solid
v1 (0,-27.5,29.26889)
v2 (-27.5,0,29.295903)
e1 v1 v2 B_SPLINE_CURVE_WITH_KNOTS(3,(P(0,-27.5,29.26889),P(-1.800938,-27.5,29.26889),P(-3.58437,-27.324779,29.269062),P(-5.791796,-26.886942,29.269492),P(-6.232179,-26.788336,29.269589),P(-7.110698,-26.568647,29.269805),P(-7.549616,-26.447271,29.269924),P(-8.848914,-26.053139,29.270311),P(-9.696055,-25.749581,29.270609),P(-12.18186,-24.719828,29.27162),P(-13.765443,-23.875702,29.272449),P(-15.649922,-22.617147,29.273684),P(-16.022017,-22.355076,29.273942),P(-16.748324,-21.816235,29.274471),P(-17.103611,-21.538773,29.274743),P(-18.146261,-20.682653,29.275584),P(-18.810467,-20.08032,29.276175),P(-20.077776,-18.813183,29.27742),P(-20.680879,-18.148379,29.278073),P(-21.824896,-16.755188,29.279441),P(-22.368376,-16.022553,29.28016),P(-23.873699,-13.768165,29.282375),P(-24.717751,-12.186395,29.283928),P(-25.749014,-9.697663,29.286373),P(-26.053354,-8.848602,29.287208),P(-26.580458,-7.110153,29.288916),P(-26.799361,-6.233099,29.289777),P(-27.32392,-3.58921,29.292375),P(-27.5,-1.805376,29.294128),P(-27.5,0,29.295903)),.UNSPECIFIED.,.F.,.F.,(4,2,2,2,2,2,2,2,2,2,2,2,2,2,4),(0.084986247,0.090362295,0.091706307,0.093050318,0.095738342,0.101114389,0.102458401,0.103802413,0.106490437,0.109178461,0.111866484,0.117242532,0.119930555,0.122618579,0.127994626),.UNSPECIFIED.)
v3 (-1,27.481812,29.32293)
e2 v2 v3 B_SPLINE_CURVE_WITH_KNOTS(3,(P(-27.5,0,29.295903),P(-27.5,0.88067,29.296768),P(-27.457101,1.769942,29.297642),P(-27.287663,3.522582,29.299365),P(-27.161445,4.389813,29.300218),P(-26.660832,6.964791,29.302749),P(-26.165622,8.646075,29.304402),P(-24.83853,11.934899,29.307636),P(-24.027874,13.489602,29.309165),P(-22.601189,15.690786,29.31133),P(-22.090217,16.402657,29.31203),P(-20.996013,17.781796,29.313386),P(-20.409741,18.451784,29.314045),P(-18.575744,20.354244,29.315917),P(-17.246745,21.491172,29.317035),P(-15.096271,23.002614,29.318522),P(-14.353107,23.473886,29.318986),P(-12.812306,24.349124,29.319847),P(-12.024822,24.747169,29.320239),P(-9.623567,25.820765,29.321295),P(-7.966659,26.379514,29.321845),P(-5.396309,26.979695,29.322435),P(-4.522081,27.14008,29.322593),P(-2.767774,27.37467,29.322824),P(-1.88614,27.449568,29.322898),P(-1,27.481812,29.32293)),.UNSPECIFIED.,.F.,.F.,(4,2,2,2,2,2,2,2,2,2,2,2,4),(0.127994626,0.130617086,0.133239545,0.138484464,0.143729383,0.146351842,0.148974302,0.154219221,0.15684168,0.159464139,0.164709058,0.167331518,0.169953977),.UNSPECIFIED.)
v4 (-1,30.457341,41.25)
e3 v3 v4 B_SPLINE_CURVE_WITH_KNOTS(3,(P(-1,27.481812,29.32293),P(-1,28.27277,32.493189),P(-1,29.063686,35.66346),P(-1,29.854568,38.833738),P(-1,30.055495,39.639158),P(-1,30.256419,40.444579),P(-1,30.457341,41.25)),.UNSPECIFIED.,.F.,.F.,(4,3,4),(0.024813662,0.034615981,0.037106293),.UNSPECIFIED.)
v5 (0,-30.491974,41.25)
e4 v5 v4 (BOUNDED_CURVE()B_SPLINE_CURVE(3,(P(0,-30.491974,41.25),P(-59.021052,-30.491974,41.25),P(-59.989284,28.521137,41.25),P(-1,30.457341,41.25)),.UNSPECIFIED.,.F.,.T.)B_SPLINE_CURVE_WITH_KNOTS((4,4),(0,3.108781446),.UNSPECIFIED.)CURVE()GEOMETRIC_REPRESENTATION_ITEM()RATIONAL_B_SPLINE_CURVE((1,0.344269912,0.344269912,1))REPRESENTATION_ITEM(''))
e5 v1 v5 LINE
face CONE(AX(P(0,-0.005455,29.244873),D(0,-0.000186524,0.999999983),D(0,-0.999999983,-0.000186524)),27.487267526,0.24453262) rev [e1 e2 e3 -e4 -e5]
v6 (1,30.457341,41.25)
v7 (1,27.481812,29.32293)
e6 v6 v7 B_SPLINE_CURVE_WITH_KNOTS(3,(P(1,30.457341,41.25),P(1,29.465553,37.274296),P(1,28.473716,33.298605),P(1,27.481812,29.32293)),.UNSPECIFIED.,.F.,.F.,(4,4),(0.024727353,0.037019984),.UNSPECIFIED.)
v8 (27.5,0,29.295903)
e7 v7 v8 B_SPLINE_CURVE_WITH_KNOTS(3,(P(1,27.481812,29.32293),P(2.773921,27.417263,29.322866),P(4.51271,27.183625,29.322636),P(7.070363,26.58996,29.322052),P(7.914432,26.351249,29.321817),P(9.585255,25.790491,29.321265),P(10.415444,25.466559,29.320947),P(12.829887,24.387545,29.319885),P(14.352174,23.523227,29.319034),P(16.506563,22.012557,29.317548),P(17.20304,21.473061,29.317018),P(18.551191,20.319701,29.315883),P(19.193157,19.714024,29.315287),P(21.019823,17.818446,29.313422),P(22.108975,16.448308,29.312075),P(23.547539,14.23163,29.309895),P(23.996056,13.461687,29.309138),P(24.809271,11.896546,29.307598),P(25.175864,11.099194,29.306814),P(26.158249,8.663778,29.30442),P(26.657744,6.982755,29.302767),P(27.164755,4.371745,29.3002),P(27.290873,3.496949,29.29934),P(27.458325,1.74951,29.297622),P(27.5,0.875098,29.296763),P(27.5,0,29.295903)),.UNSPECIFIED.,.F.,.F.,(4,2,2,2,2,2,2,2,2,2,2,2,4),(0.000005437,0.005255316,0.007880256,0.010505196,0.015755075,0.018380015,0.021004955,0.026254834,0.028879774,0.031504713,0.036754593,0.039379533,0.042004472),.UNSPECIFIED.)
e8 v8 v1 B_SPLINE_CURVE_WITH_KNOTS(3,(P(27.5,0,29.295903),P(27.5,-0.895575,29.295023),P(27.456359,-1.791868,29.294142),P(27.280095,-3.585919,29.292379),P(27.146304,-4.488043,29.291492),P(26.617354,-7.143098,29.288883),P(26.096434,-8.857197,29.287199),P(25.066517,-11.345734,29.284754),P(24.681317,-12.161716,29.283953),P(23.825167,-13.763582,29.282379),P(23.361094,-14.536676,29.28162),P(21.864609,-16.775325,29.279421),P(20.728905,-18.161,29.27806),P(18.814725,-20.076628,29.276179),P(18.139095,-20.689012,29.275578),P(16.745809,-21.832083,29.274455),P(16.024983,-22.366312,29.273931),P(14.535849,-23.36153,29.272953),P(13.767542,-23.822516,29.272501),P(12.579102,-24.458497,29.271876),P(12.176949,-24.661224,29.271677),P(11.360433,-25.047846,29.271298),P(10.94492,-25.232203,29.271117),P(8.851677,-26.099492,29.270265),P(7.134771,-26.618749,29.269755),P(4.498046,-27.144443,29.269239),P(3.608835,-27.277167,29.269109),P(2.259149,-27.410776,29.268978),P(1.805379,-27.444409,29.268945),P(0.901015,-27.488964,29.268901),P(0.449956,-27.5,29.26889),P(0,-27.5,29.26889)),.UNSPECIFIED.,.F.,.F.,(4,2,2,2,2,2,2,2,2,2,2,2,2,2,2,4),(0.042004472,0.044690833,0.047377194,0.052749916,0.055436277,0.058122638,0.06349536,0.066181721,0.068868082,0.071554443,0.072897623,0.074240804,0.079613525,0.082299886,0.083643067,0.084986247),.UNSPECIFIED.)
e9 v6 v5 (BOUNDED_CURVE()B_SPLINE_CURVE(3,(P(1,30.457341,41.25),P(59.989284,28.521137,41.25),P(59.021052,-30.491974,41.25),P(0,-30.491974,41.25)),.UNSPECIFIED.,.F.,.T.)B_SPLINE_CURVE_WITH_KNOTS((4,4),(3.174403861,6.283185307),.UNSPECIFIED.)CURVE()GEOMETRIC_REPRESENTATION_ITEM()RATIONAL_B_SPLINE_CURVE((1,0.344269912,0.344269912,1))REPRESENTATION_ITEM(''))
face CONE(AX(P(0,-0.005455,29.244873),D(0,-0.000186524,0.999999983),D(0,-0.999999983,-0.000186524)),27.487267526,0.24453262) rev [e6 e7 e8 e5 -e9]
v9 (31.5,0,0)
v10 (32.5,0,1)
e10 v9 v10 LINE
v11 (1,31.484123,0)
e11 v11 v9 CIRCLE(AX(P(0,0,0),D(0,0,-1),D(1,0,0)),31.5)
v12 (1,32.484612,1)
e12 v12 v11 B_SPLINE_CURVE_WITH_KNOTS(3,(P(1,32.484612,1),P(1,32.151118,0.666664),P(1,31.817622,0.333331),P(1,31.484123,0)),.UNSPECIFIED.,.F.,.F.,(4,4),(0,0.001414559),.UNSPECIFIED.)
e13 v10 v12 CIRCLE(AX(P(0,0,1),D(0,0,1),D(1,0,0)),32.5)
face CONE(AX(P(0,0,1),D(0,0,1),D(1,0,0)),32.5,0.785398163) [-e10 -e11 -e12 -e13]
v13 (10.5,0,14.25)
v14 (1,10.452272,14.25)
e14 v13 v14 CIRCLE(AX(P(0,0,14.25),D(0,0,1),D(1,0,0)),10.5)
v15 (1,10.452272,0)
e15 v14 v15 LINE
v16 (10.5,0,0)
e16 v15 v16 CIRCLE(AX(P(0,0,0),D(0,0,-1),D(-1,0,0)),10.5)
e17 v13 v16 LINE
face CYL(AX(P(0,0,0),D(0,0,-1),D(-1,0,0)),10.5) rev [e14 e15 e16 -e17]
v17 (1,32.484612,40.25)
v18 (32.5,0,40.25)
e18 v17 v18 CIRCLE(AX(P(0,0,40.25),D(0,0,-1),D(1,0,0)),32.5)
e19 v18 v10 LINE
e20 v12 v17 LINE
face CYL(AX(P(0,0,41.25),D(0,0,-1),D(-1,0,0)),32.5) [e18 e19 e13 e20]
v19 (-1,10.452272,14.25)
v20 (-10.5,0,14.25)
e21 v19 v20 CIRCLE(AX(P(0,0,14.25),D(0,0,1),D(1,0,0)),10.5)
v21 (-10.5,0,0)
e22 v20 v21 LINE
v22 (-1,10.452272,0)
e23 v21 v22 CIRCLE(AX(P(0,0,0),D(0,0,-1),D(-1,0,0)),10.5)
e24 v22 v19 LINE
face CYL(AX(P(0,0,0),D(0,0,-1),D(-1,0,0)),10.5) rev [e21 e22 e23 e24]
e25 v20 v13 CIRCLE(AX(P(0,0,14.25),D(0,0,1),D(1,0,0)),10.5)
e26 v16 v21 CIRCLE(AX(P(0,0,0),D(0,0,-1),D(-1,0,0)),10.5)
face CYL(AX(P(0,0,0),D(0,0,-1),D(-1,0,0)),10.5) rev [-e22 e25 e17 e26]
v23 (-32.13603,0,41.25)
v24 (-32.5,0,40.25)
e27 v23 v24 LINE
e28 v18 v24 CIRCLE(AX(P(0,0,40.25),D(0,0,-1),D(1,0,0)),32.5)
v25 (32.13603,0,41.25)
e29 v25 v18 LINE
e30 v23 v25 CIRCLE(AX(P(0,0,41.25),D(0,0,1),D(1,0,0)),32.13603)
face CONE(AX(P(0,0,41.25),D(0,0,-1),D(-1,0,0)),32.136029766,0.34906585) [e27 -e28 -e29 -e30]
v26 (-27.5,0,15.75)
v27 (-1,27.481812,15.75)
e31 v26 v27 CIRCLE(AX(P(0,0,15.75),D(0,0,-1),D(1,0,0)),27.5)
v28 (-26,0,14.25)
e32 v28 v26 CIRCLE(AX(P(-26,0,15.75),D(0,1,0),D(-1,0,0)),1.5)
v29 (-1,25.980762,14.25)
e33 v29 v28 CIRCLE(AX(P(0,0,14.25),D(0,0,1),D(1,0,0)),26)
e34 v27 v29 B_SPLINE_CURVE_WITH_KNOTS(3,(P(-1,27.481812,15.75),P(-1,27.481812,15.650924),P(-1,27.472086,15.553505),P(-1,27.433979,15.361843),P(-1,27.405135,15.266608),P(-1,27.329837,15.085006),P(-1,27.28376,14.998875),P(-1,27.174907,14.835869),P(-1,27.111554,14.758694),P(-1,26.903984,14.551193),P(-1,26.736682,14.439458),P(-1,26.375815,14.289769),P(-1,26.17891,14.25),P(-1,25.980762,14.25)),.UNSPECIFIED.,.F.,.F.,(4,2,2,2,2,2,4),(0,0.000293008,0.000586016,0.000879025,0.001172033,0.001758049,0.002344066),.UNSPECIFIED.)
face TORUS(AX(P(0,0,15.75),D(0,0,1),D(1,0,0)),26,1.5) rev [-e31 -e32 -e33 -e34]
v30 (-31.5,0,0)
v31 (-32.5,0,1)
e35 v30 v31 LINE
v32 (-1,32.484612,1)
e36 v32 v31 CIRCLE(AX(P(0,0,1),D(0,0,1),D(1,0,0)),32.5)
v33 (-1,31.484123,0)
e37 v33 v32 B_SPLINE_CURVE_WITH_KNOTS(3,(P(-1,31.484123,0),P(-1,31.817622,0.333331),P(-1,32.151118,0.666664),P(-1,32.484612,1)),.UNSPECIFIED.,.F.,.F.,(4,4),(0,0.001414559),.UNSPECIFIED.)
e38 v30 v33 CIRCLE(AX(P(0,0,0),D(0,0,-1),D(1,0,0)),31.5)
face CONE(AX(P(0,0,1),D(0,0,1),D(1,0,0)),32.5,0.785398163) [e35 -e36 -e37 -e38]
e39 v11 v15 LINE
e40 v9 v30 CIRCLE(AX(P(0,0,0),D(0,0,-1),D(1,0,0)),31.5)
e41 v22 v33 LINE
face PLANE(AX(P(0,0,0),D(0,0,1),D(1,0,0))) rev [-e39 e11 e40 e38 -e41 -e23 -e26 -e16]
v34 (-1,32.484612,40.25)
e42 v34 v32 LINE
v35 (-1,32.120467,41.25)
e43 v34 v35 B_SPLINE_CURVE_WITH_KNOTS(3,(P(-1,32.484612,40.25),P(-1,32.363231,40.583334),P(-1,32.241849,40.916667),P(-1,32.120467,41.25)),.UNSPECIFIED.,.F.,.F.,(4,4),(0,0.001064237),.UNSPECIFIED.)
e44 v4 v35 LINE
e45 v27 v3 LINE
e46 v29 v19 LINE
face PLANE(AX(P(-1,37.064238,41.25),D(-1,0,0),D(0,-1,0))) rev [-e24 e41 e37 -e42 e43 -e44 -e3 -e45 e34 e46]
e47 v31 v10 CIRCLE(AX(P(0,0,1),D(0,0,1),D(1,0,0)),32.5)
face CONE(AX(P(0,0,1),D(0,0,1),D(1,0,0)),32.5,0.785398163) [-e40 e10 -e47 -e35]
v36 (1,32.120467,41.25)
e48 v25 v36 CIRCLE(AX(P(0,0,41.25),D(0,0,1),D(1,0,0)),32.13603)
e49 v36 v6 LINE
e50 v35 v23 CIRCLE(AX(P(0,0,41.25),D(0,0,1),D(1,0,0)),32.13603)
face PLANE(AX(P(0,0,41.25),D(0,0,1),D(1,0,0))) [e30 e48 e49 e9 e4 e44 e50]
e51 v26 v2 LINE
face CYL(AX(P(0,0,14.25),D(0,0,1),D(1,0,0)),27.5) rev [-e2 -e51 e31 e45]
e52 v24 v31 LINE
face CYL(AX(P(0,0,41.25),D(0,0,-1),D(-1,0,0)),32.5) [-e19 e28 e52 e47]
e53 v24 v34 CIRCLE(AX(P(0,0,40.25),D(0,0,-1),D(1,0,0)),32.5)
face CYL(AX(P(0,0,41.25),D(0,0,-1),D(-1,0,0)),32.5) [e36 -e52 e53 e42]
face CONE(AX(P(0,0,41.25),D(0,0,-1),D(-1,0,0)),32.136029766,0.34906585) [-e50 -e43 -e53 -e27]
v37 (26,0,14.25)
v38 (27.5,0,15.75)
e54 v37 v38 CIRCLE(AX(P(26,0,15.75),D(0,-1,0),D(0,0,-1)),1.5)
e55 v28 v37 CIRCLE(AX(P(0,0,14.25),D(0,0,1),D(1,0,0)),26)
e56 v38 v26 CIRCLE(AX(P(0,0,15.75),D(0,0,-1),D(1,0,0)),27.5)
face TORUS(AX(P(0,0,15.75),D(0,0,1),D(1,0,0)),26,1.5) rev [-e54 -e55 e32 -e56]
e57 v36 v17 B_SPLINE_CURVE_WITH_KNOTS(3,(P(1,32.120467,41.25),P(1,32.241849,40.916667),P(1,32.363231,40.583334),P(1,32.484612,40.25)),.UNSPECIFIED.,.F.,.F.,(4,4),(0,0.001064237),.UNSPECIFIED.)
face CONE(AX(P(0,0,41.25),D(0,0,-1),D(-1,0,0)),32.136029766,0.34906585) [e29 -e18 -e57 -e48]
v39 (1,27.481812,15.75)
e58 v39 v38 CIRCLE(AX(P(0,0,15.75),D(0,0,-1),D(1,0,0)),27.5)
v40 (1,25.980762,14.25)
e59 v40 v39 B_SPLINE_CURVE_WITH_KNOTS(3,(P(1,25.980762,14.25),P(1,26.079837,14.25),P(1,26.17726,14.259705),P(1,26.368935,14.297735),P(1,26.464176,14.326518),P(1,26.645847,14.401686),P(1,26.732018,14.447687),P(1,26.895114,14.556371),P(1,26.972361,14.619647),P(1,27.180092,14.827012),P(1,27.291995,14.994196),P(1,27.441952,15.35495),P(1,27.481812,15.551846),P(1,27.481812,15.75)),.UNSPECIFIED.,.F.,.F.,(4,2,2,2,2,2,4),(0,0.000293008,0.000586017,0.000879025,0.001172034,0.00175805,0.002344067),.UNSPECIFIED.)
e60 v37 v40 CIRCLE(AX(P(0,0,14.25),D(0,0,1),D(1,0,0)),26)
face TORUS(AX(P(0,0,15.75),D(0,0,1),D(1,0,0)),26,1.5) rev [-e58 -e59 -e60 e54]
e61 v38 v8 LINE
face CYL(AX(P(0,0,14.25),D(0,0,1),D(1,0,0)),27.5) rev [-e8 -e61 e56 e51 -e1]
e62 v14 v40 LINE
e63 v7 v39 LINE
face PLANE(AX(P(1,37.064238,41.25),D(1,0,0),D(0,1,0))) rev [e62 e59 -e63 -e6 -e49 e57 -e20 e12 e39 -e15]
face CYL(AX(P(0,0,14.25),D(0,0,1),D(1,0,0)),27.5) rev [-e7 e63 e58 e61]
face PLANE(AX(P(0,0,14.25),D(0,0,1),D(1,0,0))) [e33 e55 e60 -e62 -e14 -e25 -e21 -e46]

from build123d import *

# Parameters (mm, degrees)
SKETCH_1_R          = 32.5
EXTRUDE_1_DEPTH     = 41.25
SKETCH_2_R          = 27.5
CUT_EXTRUDE_1_DEPTH = 27
HOLE_WIZARD_M24_1_D = 21
SKETCH_4_W          = 2
SKETCH_4_H          = 41.62847608
CUT_EXTRUDE_2_DEPTH = 62.758096635
CHAMFER_1_SIZE      = 1
CHAMFER_2_SIZE      = 1
CHAMFER_2_SIZE2     = 0.363970234
FILLET_1_R          = 1.5


with BuildPart() as part:
    # 草图1 → 凸台-拉伸1 (new body)
    with BuildSketch(Plane.XY):
        Circle(SKETCH_1_R)
    extrude(amount=EXTRUDE_1_DEPTH)

    # 草图2 → 切除-拉伸1 (cut)
    with BuildSketch(Plane.XY.offset(41.25)):
        Circle(SKETCH_2_R)
    extrude(amount=-CUT_EXTRUDE_1_DEPTH, mode=Mode.SUBTRACT)

    # M24 螺纹孔1 (through all)
    with Locations(Plane(origin=(0, 0, 0), x_dir=(-1, 0, 0), z_dir=(0, 0, -1))):
        with Locations((0, 0)):
            Hole(HOLE_WIZARD_M24_1_D / 2)

    # 草图4 → 切除-拉伸2 (cut, through all)
    with BuildSketch(Plane(origin=(0, 0, 0), x_dir=(-1, 0, 0), z_dir=(0, 0, -1))):
        with Locations((0, 16.25)):
            Rectangle(SKETCH_4_W, SKETCH_4_H)
    extrude(amount=-CUT_EXTRUDE_2_DEPTH, mode=Mode.SUBTRACT)

    # 草图5 → 切除-旋转1 (revolve, cut)
    with BuildSketch(Plane(origin=(0, 0, 0), x_dir=(0, 0, -1), z_dir=(1, 0, 0))):
        Polygon((-44.25, 27.481812167), (-29.25, 27.481812167), (-44.25, 31.22173221), align=None)
    revolve(axis=Axis((0, -0.007694129, 41.25), (0, 0.00018652434146350927, -0.9999999826043349)), mode=Mode.SUBTRACT)

    # 倒角1
    chamfer_1_edges = [part.edges().sort_by_distance(p)[0] for p in [
        (-22.624654693, -23.331845191, 0),
    ]]
    chamfer(chamfer_1_edges, length=CHAMFER_1_SIZE)

    # 倒角2
    chamfer_2_edges = [part.edges().sort_by_distance(p)[0] for p in [
        (-22.624654693, -23.331845191, 41.25),
    ]]
    chamfer_2_side = [part.faces().sort_by_distance(p)[0] for p in [
        (-22.624654693, -23.331845191, 21.125),
    ]]
    chamfer(chamfer_2_edges, length=CHAMFER_2_SIZE, length2=CHAMFER_2_SIZE2, reference=chamfer_2_side[0])

    # 圆角1
    fillet_1_edges = [part.edges().sort_by_distance(p)[0] for p in [
        (-19.088609169, -19.795832895, 14.25),
    ]]
    fillet(fillet_1_edges, radius=FILLET_1_R)


solid = part.part
